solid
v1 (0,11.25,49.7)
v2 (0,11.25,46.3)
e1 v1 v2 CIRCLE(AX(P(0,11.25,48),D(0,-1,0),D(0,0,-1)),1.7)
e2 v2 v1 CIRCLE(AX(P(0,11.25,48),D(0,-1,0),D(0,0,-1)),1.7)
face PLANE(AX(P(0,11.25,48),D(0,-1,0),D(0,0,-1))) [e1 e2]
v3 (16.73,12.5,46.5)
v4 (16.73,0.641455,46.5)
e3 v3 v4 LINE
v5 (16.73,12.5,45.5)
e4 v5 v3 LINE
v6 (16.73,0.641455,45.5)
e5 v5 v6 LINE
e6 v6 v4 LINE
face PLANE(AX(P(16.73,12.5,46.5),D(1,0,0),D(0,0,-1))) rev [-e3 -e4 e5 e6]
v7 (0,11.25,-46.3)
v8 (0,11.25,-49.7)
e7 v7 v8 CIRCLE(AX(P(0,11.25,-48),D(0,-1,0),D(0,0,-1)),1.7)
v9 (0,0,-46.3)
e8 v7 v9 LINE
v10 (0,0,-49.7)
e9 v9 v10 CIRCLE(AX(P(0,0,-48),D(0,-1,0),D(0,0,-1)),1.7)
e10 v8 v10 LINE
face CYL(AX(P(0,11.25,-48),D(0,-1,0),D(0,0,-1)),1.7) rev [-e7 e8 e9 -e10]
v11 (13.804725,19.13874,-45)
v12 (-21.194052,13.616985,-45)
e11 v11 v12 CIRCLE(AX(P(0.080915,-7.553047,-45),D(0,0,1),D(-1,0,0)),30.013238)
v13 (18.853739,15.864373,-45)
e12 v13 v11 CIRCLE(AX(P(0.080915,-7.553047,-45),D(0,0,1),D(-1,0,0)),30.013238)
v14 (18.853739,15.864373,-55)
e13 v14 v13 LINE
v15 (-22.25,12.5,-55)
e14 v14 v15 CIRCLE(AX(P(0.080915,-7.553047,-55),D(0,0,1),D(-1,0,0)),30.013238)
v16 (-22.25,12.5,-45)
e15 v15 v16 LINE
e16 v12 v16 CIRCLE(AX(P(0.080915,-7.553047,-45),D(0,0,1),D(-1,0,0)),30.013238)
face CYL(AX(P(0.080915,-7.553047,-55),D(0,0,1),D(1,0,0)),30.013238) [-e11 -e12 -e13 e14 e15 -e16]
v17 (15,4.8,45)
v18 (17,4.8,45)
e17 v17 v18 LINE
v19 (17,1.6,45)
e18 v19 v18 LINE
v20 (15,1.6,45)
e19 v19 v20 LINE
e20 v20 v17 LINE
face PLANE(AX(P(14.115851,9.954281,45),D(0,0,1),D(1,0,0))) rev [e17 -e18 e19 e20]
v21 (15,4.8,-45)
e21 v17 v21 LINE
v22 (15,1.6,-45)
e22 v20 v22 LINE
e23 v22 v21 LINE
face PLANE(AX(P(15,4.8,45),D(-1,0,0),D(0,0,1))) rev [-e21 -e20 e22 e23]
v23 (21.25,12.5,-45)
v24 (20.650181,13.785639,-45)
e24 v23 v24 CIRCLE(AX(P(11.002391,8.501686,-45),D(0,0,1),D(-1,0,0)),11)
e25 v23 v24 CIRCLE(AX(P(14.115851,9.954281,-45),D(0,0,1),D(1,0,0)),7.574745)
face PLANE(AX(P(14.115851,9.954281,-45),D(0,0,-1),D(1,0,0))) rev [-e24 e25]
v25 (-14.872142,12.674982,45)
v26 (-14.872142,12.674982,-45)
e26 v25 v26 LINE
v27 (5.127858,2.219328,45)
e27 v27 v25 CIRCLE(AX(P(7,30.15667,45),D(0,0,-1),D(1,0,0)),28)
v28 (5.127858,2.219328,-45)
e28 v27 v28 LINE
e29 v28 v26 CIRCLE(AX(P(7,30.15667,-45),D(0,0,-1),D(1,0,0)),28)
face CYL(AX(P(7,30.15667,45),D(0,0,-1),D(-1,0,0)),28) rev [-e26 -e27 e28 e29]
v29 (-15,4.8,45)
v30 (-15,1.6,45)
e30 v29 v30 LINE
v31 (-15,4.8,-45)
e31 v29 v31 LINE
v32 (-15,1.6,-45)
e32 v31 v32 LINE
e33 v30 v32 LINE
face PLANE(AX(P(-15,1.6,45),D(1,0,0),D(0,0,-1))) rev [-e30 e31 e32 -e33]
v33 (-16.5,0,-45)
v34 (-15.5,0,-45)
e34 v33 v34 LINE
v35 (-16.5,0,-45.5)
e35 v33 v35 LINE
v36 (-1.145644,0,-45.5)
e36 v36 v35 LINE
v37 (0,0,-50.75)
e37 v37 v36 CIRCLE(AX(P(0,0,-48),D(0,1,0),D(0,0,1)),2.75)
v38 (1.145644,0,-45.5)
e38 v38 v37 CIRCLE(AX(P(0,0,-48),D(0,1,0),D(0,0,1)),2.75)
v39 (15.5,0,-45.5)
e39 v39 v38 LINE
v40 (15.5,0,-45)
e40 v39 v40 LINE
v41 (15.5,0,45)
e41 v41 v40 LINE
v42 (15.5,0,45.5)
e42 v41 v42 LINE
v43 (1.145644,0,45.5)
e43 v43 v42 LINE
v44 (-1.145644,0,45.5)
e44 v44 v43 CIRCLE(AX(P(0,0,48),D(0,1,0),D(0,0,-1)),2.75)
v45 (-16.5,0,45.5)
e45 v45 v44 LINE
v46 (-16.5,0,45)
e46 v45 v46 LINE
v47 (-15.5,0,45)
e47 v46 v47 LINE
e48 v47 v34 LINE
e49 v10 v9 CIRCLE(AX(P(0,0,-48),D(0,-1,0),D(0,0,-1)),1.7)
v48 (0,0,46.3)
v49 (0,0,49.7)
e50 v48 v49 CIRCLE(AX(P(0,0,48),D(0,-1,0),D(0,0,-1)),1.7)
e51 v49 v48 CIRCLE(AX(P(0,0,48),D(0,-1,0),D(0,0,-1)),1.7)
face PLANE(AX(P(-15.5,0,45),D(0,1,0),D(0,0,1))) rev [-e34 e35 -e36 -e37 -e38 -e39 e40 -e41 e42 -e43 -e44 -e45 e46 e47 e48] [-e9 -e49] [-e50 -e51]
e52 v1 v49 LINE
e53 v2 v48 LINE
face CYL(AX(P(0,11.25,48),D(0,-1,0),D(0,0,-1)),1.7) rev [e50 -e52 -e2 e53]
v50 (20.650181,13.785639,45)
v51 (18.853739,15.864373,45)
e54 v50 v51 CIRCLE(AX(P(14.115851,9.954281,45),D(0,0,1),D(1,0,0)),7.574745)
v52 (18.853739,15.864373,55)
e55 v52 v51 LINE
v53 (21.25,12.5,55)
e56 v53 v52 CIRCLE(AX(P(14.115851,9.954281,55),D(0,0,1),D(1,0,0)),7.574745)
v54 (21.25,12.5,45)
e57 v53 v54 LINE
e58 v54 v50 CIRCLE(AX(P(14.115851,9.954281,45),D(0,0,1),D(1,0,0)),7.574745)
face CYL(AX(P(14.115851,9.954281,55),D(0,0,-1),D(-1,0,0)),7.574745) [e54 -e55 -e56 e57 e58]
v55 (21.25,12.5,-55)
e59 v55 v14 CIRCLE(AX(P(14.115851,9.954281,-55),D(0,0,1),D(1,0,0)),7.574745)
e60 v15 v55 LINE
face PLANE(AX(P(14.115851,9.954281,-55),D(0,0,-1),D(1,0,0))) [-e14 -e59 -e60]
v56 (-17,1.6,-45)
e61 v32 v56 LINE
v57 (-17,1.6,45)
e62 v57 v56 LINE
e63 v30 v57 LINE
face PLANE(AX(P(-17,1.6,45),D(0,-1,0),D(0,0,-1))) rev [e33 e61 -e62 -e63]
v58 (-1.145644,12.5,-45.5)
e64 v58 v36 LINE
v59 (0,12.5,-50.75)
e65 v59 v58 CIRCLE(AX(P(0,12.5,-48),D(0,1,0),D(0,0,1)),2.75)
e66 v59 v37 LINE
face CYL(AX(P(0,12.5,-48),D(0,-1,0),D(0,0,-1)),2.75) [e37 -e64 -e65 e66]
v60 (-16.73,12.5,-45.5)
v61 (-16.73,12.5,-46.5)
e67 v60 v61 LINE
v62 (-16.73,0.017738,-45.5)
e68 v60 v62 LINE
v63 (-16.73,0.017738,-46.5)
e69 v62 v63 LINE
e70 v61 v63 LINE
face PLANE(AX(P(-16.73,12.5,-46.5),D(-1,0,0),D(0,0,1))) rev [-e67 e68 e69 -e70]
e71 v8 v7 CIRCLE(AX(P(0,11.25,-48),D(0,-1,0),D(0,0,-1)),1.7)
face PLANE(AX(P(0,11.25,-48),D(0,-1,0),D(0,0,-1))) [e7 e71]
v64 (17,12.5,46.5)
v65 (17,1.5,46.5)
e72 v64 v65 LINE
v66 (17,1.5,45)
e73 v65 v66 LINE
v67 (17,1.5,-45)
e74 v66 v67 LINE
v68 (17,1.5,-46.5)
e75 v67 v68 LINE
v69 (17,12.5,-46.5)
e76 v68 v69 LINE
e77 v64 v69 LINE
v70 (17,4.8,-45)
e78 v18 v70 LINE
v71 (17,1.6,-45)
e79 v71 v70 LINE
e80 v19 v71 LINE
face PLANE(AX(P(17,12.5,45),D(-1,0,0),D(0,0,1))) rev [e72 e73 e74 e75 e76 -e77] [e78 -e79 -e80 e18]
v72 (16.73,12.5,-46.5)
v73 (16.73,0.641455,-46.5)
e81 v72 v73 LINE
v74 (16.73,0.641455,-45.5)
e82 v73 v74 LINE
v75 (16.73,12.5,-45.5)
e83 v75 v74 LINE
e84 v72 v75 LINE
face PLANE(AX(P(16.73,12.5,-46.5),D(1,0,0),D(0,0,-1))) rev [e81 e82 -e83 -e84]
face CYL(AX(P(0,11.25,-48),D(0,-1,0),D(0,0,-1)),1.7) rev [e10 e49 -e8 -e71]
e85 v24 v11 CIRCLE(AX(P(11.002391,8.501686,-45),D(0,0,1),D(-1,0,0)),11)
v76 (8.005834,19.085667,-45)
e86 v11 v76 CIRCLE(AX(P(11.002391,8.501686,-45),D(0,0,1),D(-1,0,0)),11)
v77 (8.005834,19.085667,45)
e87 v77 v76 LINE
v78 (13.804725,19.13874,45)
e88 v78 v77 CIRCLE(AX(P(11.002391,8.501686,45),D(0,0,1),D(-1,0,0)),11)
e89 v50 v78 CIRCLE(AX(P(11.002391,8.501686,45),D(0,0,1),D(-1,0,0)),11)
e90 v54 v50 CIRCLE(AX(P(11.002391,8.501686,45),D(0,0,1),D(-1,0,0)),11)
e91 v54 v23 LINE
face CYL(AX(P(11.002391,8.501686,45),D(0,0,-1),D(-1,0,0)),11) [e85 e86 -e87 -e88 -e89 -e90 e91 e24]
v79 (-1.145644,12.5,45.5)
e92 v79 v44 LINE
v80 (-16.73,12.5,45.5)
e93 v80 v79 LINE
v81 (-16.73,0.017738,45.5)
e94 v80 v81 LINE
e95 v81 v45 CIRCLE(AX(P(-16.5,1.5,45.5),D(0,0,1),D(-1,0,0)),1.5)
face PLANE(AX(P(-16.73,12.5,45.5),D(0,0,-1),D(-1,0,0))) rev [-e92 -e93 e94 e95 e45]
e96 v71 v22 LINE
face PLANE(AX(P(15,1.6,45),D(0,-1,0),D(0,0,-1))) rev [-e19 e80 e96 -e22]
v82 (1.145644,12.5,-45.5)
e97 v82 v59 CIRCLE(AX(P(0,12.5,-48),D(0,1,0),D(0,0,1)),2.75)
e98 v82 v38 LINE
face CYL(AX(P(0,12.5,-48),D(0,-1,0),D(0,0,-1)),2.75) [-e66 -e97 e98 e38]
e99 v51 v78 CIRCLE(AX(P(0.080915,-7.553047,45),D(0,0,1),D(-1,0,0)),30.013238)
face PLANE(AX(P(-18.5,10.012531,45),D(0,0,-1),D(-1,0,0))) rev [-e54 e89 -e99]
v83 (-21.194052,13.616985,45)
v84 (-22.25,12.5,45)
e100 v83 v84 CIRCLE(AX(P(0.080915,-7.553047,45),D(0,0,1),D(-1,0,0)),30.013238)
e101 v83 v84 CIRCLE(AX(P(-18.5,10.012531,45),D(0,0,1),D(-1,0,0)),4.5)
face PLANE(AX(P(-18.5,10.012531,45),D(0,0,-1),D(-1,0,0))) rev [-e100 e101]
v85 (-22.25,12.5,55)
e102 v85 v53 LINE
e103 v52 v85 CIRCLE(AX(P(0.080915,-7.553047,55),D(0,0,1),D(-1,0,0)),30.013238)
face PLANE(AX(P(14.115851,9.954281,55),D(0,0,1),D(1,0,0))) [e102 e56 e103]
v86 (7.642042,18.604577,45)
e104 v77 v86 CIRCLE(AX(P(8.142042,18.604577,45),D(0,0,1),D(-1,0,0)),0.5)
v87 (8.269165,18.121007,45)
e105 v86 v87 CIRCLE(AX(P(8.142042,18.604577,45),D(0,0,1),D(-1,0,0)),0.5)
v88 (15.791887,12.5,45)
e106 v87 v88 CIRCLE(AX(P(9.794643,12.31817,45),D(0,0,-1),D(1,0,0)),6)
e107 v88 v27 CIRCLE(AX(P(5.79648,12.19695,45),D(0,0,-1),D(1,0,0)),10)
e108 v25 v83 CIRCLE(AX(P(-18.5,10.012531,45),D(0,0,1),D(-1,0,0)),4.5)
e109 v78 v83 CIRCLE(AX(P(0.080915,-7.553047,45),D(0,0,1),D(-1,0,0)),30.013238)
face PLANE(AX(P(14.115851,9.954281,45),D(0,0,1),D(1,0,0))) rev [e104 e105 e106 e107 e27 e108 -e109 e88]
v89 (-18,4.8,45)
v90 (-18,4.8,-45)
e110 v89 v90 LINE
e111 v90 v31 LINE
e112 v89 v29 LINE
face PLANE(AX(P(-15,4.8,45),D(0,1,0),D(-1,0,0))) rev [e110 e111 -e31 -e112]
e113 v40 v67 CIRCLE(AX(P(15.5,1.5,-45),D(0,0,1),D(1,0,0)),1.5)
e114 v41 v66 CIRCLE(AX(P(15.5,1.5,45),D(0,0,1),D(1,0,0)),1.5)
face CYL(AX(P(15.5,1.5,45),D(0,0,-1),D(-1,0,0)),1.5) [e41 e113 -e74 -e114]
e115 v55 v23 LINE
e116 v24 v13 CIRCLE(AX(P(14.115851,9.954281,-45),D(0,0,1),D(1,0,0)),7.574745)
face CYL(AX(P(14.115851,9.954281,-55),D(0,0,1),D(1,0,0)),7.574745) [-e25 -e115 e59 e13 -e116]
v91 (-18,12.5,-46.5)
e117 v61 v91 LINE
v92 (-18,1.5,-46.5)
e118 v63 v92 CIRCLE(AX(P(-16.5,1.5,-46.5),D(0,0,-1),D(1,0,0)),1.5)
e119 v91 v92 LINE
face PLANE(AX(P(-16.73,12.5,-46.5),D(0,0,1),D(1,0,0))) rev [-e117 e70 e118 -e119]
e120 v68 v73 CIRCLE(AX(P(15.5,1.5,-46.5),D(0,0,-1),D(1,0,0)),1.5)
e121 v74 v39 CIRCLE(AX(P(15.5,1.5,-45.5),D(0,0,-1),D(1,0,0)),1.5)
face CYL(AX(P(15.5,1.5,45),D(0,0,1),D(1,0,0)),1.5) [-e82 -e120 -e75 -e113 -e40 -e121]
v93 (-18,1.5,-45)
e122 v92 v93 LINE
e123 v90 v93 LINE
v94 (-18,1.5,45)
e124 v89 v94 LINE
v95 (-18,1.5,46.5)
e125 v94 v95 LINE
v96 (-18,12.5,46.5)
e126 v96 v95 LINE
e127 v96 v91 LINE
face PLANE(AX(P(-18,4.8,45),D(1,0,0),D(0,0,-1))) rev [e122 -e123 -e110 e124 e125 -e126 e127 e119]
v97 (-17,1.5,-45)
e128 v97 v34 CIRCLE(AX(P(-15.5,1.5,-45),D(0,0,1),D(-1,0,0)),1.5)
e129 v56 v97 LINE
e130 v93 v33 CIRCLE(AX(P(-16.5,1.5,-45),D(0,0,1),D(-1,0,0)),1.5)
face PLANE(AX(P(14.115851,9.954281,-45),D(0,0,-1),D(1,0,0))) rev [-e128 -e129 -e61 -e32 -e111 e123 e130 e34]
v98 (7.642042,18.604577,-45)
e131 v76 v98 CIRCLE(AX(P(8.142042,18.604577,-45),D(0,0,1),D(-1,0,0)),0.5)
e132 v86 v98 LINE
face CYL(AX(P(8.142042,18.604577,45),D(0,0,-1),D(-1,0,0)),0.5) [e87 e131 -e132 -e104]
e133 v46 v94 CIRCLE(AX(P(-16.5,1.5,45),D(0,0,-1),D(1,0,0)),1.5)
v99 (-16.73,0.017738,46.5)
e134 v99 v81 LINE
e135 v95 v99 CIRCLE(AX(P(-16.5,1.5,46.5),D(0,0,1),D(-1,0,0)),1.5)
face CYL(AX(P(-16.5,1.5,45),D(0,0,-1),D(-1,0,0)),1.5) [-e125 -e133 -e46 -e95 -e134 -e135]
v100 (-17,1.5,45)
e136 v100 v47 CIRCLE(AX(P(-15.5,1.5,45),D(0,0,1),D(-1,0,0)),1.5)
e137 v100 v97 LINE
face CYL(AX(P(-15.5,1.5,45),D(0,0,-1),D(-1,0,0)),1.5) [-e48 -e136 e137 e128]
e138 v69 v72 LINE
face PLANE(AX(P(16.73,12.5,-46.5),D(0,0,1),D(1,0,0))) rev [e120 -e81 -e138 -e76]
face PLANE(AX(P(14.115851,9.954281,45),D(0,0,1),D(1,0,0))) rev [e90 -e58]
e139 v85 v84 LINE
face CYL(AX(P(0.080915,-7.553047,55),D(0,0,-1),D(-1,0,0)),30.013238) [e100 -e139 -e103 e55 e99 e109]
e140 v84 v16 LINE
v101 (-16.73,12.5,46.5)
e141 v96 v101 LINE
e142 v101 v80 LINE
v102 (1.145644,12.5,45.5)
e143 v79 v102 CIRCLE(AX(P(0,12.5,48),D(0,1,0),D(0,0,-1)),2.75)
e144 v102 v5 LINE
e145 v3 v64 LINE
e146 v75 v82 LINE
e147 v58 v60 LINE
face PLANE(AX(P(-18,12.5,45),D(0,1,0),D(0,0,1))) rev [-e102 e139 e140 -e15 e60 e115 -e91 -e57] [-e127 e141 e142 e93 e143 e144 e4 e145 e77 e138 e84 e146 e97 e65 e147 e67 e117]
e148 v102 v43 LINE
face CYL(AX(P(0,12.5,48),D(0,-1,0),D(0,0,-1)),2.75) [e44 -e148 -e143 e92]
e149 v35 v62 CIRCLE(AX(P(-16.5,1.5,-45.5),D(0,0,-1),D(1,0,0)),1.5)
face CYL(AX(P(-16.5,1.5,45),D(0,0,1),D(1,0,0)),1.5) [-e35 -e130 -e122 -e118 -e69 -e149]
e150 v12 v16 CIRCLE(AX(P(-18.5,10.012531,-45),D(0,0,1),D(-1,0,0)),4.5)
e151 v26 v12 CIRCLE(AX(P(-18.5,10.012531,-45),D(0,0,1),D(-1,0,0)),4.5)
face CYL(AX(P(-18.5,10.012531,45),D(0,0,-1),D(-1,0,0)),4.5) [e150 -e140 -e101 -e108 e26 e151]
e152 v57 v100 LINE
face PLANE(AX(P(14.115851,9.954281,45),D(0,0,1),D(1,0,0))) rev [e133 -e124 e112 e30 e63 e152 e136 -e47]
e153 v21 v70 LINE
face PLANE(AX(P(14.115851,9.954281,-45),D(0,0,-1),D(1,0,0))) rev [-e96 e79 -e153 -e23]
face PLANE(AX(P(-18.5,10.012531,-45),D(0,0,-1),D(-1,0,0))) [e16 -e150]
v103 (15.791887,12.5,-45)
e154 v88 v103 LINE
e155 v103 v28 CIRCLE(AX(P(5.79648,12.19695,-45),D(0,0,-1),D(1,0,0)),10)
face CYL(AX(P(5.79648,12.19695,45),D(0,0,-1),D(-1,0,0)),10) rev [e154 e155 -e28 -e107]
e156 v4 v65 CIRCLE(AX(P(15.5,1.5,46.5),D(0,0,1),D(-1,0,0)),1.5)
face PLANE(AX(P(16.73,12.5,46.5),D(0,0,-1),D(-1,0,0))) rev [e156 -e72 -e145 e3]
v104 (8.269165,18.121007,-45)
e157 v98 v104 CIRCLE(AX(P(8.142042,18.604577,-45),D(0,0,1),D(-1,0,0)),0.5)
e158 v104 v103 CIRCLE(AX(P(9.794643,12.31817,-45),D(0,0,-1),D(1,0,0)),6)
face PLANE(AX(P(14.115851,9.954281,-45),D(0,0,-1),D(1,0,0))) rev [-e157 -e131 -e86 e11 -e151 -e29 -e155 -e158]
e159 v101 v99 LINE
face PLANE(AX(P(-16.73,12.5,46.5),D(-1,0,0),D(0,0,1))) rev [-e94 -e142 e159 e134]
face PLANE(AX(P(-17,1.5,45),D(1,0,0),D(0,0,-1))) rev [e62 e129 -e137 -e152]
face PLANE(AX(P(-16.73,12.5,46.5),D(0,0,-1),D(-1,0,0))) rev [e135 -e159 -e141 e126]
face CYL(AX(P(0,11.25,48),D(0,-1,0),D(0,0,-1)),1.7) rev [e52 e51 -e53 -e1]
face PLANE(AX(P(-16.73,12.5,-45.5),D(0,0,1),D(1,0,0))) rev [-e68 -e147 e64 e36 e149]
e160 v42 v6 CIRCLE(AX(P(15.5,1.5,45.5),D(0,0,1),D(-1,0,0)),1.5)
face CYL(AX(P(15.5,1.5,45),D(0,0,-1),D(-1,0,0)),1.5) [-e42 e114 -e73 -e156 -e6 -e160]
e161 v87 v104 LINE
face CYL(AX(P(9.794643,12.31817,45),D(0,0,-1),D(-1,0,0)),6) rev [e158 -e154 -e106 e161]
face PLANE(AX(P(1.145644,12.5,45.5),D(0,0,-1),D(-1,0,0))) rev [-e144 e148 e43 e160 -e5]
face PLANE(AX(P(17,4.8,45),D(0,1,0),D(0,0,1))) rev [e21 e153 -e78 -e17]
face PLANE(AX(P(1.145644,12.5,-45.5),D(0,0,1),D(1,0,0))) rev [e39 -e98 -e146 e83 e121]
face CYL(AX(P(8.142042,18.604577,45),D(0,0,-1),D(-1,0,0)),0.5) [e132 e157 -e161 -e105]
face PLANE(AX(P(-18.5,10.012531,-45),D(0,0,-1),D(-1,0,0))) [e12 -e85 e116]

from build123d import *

# Parameters (mm, degrees)
EXTRUDE_1_DEPTH      = 45
EXTRUDE_2_DEPTH      = 10
CUT_EXTRUDE_11_DEPTH = 12.5
FILLET_1_R           = 1.5
SKETCH_4_R           = 1.7
CUT_EXTRUDE_12_DEPTH = 11.25


with BuildPart() as part:
    # 草图1 → 凸台-拉伸1 (new, symmetric)
    with BuildSketch(Plane.XY):
        with BuildLine():
            Line((-15.5, 0), (15.5, 0))
            ThreePointArc((15.5, 0), (16.560660172, 0.439339828), (17, 1.5))
            Line((17, 1.5), (17, 1.6))
            Line((17, 1.6), (15, 1.6))
            Line((15, 1.6), (15, 4.8))
            Line((15, 4.8), (17, 4.8))
            Line((17, 4.8), (17, 12.5))
            Line((17, 12.5), (21.25, 12.5))
            ThreePointArc((21.25, 12.5), (15.900063146, 18.351194202), (8.005834372, 19.085666803))
            ThreePointArc((8.005834372, 19.085666803), (7.659690231, 18.472905768), (8.269164703, 18.121007034))
            ThreePointArc((8.269164703, 18.121007034), (13.386035944, 17.124613538), (15.791887335, 12.5))
            ThreePointArc((15.791887335, 12.5), (12.736961816, 4.997664438), (5.127858316, 2.219328112))
            ThreePointArc((5.127858316, 2.219328112), (-5.972198102, 5.342922516), (-14.872141684, 12.674982166))
            ThreePointArc((-14.872141684, 12.674982166), (-18.60669741, 14.511266303), (-22.25, 12.5))
            Line((-22.25, 12.5), (-18, 12.5))
            Line((-18, 12.5), (-18, 4.8))
            Line((-18, 4.8), (-15, 4.8))
            Line((-15, 4.8), (-15, 1.6))
            Line((-15, 1.6), (-17, 1.6))
            Line((-17, 1.6), (-17, 1.5))
            ThreePointArc((-17, 1.5), (-16.560660172, 0.439339828), (-15.5, 0))
        make_face()
    extrude(amount=EXTRUDE_1_DEPTH, both=True)

    # 草图2 → 凸台-拉伸2 (add)
    with BuildSketch(Plane.XY.offset(45)):
        with BuildLine():
            Line((-22.25, 12.5), (-18, 12.5))
            Line((-18, 12.5), (-18, 1.5))
            Line((-18, 1.5), (-18, 0))
            Line((-18, 0), (-16.5, 0))
            Line((-16.5, 0), (16.5, 0))
            Line((16.5, 0), (17, 0))
            Line((17, 0), (17, 1.5))
            Line((17, 1.5), (17, 12.5))
            Line((17, 12.5), (21.25, 12.5))
            ThreePointArc((21.25, 12.5), (20.28562135, 14.348675496), (18.853738793, 15.864373227))
            ThreePointArc((18.853738793, 15.864373227), (-2.367503819, 22.360156158), (-22.25, 12.5))
        make_face()
    extrude_2 = extrude(amount=EXTRUDE_2_DEPTH)

    # 镜向1: 凸台-拉伸2 across plane
    add(extrude_2.mirror(Plane.XY))

    # 草图3 → 切除-拉伸11 (cut)
    with BuildSketch(Plane.XZ):
        with BuildLine():
            Line((1.145643924, 45.5), (16.73, 45.5))
            Line((16.73, 45.5), (16.73, 46.5))
            Line((16.73, 46.5), (18, 46.5))
            Line((18, 46.5), (18, 55))
            Line((18, 55), (-18, 55))
            Line((-18, 55), (-18, 46.5))
            Line((-18, 46.5), (-16.73, 46.5))
            Line((-16.73, 46.5), (-16.73, 45.5))
            Line((-16.73, 45.5), (-1.145643924, 45.5))
            ThreePointArc((-1.145643924, 45.5), (0, 50.75), (1.145643924, 45.5))
        make_face()
        with BuildLine():
            Line((-18, -46.5), (-18, -55))
            Line((-18, -55), (18, -55))
            Line((18, -55), (18, -46.5))
            Line((18, -46.5), (16.73, -46.5))
            Line((16.73, -46.5), (16.73, -45.5))
            Line((16.73, -45.5), (1.145643924, -45.5))
            ThreePointArc((1.145643924, -45.5), (0, -50.75), (-1.145643924, -45.5))
            Line((-1.145643924, -45.5), (-16.73, -45.5))
            Line((-16.73, -45.5), (-16.73, -46.5))
            Line((-16.73, -46.5), (-18, -46.5))
        make_face()
    extrude(amount=-CUT_EXTRUDE_11_DEPTH, mode=Mode.SUBTRACT)

    # 圆角1
    fillet_1_edges = [part.edges().sort_by_distance(p)[0] for p in [
        (-18, 0, -45.75),
        (17, 0, -45.75),
        (17, 0, 45.75),
        (-18, 0, 45.75),
    ]]
    fillet(fillet_1_edges, radius=FILLET_1_R)

    # 草图4 → 切除-拉伸12 (cut)
    with BuildSketch(Plane.XZ):
        with Locations(Location((0, 48, 0), (0, 0, 270))):
            Circle(SKETCH_4_R)
        with Locations(Location((0, -48, 0), (0, 0, 270))):
            Circle(SKETCH_4_R)
    extrude(amount=-CUT_EXTRUDE_12_DEPTH, mode=Mode.SUBTRACT)


solid = part.part
